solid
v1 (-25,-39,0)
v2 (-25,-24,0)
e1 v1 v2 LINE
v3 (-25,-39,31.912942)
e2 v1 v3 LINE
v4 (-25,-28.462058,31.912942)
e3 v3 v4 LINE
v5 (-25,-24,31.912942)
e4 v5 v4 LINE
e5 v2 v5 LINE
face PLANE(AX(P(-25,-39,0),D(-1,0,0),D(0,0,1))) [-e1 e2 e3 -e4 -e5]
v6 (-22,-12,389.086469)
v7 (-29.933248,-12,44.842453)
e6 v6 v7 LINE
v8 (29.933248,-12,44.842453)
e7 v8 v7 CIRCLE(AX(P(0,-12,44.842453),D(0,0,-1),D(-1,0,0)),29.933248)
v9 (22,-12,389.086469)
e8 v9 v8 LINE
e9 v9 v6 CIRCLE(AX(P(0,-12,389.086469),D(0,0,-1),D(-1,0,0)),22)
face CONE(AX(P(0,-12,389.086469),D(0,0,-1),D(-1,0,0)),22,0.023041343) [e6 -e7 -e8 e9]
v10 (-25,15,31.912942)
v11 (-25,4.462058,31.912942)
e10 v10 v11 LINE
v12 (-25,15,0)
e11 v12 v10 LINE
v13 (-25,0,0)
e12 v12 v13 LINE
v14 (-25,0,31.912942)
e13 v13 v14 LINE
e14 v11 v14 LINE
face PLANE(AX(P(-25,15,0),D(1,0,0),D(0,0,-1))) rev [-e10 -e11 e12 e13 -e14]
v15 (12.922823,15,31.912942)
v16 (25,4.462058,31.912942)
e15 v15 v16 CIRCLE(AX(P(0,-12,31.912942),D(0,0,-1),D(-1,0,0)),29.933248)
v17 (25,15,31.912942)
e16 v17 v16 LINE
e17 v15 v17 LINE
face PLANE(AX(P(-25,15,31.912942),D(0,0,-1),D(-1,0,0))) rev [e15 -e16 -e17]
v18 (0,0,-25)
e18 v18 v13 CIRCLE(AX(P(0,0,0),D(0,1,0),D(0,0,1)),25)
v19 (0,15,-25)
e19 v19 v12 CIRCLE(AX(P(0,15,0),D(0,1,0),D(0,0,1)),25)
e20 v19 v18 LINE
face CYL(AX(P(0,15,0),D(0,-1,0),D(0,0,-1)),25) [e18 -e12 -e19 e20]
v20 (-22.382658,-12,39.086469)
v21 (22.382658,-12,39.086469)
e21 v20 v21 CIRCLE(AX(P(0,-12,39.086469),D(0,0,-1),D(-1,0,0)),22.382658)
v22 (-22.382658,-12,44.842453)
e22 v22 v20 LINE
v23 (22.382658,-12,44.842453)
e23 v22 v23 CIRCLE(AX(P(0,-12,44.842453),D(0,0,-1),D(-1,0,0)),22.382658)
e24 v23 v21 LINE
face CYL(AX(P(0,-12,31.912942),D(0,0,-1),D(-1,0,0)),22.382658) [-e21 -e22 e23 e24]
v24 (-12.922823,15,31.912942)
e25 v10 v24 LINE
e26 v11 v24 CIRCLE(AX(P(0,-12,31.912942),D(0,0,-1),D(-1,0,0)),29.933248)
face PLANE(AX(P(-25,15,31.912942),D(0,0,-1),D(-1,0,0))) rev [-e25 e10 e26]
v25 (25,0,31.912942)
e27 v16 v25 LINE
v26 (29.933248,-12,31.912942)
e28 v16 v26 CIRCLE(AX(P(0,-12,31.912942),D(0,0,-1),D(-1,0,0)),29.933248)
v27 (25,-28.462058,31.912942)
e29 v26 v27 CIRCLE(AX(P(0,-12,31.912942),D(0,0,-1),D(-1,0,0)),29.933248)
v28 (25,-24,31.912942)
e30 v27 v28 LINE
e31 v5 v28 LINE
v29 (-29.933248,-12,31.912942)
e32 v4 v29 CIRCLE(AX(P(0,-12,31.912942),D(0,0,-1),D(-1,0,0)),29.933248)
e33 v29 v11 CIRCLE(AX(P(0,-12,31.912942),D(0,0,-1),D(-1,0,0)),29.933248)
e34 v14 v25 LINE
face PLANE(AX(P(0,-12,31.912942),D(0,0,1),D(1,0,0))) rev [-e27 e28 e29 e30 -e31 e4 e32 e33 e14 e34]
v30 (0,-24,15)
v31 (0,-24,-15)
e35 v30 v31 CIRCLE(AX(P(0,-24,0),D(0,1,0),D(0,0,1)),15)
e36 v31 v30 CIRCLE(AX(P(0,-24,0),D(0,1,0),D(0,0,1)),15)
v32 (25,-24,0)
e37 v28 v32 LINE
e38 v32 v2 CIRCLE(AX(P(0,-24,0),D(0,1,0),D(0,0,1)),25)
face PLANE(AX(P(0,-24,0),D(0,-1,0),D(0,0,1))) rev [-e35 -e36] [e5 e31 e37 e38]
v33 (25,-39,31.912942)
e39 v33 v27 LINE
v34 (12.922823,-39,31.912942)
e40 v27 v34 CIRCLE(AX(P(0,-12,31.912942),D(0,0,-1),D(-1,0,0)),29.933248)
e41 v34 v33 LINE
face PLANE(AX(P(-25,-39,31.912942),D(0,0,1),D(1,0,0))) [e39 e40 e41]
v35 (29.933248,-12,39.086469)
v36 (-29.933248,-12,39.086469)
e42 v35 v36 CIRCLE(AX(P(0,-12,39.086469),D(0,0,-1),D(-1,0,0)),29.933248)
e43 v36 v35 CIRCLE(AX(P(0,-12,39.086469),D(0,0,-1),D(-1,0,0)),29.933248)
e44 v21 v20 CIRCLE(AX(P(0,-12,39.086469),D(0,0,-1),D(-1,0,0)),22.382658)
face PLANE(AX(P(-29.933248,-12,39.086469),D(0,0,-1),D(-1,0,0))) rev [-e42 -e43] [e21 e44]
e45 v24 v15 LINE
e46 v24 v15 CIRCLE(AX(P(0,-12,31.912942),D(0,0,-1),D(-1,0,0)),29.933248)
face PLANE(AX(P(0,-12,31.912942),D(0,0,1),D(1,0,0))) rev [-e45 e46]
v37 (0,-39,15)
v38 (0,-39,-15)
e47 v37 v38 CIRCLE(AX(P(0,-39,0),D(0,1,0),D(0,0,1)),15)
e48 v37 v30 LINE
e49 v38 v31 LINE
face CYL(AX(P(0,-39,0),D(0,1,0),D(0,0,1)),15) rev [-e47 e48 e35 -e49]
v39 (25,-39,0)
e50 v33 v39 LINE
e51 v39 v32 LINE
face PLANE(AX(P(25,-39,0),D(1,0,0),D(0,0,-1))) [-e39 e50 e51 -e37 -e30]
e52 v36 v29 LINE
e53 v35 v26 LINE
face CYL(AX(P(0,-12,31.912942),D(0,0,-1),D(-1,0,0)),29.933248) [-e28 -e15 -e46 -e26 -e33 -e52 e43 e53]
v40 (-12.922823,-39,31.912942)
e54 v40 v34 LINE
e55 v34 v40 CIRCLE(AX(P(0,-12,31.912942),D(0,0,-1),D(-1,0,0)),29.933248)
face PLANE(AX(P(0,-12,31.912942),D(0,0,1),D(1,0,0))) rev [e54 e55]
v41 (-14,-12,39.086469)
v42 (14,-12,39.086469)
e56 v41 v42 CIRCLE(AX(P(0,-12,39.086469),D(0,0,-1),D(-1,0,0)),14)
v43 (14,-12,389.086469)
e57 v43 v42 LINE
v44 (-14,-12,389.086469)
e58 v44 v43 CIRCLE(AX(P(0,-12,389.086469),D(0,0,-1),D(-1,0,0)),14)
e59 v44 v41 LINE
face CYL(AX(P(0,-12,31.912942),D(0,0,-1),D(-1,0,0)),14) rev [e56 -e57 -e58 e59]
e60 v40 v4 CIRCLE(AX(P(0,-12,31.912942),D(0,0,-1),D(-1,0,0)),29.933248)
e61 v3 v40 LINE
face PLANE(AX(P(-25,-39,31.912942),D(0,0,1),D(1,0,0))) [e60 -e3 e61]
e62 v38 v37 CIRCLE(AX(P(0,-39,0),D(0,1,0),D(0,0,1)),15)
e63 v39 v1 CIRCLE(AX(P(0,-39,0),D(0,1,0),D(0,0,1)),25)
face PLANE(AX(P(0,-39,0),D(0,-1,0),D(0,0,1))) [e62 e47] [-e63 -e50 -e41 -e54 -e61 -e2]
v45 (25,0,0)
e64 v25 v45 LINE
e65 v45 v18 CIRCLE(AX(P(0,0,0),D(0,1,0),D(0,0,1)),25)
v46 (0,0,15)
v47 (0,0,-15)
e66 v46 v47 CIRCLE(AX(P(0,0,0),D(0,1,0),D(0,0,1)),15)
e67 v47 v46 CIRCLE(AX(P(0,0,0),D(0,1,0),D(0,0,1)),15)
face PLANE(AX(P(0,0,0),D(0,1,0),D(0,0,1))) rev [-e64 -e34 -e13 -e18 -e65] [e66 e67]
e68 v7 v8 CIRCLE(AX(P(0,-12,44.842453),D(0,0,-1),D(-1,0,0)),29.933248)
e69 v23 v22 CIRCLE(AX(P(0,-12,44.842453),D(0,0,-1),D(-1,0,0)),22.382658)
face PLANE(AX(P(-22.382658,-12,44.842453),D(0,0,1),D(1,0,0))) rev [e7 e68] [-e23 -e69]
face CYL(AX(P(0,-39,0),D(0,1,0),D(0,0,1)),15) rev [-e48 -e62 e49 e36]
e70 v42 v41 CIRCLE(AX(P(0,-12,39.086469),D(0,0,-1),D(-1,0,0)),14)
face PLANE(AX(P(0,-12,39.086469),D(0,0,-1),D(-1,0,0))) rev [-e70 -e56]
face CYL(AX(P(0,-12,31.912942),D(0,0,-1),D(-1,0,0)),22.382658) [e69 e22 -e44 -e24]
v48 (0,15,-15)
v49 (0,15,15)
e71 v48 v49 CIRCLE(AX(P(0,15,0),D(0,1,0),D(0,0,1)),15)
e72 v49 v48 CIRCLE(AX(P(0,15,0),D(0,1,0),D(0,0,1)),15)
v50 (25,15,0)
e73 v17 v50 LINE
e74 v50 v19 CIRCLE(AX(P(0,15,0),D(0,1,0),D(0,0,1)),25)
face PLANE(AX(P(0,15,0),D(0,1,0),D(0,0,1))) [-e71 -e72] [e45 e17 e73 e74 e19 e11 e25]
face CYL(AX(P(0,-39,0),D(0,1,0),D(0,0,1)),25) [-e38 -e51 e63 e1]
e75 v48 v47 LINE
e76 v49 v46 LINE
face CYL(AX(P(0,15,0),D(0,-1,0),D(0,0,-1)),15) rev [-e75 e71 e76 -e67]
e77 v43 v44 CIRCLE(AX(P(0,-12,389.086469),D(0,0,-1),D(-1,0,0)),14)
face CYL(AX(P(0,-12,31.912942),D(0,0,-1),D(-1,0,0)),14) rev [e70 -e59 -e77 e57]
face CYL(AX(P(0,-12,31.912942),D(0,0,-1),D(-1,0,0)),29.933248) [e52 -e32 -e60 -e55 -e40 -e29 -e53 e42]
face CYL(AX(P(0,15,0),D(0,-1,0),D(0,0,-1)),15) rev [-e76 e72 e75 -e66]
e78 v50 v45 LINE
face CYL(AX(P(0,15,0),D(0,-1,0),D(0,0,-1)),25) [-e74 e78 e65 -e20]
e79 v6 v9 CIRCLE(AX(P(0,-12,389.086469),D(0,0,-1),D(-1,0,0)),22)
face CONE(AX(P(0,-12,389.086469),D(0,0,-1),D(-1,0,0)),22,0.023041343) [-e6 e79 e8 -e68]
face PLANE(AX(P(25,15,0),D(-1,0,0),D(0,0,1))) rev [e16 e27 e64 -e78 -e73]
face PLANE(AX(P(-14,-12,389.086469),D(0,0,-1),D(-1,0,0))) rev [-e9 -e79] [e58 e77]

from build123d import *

# Parameters (mm, degrees)
SKETCH2_R           = 15
BOSS_EXTRUDE1_DEPTH = 15


with BuildPart() as part:
    # Sketch2 → Boss-Extrude1 (new body)
    with BuildSketch(Plane(origin=(0, 0, 0), x_dir=(1, 0, 0), z_dir=(0, 1, 0))):
        with BuildLine():
            Line((25, 0), (25, -31.912942224))
            Line((25, -31.912942224), (-25, -31.912942224))
            Line((-25, -31.912942224), (-25, 0))
            ThreePointArc((-25, 0), (0, 25), (25, 0))
        make_face()
        with Locations(Location((0, 0, 0), (0, 0, 270))):
            Circle(SKETCH2_R, mode=Mode.SUBTRACT)
    boss_extrude1 = extrude(amount=BOSS_EXTRUDE1_DEPTH)

    # Sketch4 → Revolve1 (revolve)
    with BuildSketch(Plane(origin=(0, -12, 0), x_dir=(-1, 0, 0), z_dir=(0, -1, 0))):
        Polygon((0, -31.912942224), (29.933248422, -31.912942224), (29.933248422, -39.086469166), (22.382657632, -39.086469166), (22.382657632, -44.842453341), (29.933248422, -44.842453341), (22, -389.086469166), (14, -389.086469166), (14, -39.086469166), (0, -39.086469166), align=None)
    revolve(axis=Axis((0, -12, 31.912942224), (0, 0, 1)))

    # Mirror5: Boss-Extrude1 across plane
    add(boss_extrude1.mirror(Plane(origin=(0, -12, 0), x_dir=(0, 0, 1), z_dir=(0, -1, 0))))


solid = part.part
